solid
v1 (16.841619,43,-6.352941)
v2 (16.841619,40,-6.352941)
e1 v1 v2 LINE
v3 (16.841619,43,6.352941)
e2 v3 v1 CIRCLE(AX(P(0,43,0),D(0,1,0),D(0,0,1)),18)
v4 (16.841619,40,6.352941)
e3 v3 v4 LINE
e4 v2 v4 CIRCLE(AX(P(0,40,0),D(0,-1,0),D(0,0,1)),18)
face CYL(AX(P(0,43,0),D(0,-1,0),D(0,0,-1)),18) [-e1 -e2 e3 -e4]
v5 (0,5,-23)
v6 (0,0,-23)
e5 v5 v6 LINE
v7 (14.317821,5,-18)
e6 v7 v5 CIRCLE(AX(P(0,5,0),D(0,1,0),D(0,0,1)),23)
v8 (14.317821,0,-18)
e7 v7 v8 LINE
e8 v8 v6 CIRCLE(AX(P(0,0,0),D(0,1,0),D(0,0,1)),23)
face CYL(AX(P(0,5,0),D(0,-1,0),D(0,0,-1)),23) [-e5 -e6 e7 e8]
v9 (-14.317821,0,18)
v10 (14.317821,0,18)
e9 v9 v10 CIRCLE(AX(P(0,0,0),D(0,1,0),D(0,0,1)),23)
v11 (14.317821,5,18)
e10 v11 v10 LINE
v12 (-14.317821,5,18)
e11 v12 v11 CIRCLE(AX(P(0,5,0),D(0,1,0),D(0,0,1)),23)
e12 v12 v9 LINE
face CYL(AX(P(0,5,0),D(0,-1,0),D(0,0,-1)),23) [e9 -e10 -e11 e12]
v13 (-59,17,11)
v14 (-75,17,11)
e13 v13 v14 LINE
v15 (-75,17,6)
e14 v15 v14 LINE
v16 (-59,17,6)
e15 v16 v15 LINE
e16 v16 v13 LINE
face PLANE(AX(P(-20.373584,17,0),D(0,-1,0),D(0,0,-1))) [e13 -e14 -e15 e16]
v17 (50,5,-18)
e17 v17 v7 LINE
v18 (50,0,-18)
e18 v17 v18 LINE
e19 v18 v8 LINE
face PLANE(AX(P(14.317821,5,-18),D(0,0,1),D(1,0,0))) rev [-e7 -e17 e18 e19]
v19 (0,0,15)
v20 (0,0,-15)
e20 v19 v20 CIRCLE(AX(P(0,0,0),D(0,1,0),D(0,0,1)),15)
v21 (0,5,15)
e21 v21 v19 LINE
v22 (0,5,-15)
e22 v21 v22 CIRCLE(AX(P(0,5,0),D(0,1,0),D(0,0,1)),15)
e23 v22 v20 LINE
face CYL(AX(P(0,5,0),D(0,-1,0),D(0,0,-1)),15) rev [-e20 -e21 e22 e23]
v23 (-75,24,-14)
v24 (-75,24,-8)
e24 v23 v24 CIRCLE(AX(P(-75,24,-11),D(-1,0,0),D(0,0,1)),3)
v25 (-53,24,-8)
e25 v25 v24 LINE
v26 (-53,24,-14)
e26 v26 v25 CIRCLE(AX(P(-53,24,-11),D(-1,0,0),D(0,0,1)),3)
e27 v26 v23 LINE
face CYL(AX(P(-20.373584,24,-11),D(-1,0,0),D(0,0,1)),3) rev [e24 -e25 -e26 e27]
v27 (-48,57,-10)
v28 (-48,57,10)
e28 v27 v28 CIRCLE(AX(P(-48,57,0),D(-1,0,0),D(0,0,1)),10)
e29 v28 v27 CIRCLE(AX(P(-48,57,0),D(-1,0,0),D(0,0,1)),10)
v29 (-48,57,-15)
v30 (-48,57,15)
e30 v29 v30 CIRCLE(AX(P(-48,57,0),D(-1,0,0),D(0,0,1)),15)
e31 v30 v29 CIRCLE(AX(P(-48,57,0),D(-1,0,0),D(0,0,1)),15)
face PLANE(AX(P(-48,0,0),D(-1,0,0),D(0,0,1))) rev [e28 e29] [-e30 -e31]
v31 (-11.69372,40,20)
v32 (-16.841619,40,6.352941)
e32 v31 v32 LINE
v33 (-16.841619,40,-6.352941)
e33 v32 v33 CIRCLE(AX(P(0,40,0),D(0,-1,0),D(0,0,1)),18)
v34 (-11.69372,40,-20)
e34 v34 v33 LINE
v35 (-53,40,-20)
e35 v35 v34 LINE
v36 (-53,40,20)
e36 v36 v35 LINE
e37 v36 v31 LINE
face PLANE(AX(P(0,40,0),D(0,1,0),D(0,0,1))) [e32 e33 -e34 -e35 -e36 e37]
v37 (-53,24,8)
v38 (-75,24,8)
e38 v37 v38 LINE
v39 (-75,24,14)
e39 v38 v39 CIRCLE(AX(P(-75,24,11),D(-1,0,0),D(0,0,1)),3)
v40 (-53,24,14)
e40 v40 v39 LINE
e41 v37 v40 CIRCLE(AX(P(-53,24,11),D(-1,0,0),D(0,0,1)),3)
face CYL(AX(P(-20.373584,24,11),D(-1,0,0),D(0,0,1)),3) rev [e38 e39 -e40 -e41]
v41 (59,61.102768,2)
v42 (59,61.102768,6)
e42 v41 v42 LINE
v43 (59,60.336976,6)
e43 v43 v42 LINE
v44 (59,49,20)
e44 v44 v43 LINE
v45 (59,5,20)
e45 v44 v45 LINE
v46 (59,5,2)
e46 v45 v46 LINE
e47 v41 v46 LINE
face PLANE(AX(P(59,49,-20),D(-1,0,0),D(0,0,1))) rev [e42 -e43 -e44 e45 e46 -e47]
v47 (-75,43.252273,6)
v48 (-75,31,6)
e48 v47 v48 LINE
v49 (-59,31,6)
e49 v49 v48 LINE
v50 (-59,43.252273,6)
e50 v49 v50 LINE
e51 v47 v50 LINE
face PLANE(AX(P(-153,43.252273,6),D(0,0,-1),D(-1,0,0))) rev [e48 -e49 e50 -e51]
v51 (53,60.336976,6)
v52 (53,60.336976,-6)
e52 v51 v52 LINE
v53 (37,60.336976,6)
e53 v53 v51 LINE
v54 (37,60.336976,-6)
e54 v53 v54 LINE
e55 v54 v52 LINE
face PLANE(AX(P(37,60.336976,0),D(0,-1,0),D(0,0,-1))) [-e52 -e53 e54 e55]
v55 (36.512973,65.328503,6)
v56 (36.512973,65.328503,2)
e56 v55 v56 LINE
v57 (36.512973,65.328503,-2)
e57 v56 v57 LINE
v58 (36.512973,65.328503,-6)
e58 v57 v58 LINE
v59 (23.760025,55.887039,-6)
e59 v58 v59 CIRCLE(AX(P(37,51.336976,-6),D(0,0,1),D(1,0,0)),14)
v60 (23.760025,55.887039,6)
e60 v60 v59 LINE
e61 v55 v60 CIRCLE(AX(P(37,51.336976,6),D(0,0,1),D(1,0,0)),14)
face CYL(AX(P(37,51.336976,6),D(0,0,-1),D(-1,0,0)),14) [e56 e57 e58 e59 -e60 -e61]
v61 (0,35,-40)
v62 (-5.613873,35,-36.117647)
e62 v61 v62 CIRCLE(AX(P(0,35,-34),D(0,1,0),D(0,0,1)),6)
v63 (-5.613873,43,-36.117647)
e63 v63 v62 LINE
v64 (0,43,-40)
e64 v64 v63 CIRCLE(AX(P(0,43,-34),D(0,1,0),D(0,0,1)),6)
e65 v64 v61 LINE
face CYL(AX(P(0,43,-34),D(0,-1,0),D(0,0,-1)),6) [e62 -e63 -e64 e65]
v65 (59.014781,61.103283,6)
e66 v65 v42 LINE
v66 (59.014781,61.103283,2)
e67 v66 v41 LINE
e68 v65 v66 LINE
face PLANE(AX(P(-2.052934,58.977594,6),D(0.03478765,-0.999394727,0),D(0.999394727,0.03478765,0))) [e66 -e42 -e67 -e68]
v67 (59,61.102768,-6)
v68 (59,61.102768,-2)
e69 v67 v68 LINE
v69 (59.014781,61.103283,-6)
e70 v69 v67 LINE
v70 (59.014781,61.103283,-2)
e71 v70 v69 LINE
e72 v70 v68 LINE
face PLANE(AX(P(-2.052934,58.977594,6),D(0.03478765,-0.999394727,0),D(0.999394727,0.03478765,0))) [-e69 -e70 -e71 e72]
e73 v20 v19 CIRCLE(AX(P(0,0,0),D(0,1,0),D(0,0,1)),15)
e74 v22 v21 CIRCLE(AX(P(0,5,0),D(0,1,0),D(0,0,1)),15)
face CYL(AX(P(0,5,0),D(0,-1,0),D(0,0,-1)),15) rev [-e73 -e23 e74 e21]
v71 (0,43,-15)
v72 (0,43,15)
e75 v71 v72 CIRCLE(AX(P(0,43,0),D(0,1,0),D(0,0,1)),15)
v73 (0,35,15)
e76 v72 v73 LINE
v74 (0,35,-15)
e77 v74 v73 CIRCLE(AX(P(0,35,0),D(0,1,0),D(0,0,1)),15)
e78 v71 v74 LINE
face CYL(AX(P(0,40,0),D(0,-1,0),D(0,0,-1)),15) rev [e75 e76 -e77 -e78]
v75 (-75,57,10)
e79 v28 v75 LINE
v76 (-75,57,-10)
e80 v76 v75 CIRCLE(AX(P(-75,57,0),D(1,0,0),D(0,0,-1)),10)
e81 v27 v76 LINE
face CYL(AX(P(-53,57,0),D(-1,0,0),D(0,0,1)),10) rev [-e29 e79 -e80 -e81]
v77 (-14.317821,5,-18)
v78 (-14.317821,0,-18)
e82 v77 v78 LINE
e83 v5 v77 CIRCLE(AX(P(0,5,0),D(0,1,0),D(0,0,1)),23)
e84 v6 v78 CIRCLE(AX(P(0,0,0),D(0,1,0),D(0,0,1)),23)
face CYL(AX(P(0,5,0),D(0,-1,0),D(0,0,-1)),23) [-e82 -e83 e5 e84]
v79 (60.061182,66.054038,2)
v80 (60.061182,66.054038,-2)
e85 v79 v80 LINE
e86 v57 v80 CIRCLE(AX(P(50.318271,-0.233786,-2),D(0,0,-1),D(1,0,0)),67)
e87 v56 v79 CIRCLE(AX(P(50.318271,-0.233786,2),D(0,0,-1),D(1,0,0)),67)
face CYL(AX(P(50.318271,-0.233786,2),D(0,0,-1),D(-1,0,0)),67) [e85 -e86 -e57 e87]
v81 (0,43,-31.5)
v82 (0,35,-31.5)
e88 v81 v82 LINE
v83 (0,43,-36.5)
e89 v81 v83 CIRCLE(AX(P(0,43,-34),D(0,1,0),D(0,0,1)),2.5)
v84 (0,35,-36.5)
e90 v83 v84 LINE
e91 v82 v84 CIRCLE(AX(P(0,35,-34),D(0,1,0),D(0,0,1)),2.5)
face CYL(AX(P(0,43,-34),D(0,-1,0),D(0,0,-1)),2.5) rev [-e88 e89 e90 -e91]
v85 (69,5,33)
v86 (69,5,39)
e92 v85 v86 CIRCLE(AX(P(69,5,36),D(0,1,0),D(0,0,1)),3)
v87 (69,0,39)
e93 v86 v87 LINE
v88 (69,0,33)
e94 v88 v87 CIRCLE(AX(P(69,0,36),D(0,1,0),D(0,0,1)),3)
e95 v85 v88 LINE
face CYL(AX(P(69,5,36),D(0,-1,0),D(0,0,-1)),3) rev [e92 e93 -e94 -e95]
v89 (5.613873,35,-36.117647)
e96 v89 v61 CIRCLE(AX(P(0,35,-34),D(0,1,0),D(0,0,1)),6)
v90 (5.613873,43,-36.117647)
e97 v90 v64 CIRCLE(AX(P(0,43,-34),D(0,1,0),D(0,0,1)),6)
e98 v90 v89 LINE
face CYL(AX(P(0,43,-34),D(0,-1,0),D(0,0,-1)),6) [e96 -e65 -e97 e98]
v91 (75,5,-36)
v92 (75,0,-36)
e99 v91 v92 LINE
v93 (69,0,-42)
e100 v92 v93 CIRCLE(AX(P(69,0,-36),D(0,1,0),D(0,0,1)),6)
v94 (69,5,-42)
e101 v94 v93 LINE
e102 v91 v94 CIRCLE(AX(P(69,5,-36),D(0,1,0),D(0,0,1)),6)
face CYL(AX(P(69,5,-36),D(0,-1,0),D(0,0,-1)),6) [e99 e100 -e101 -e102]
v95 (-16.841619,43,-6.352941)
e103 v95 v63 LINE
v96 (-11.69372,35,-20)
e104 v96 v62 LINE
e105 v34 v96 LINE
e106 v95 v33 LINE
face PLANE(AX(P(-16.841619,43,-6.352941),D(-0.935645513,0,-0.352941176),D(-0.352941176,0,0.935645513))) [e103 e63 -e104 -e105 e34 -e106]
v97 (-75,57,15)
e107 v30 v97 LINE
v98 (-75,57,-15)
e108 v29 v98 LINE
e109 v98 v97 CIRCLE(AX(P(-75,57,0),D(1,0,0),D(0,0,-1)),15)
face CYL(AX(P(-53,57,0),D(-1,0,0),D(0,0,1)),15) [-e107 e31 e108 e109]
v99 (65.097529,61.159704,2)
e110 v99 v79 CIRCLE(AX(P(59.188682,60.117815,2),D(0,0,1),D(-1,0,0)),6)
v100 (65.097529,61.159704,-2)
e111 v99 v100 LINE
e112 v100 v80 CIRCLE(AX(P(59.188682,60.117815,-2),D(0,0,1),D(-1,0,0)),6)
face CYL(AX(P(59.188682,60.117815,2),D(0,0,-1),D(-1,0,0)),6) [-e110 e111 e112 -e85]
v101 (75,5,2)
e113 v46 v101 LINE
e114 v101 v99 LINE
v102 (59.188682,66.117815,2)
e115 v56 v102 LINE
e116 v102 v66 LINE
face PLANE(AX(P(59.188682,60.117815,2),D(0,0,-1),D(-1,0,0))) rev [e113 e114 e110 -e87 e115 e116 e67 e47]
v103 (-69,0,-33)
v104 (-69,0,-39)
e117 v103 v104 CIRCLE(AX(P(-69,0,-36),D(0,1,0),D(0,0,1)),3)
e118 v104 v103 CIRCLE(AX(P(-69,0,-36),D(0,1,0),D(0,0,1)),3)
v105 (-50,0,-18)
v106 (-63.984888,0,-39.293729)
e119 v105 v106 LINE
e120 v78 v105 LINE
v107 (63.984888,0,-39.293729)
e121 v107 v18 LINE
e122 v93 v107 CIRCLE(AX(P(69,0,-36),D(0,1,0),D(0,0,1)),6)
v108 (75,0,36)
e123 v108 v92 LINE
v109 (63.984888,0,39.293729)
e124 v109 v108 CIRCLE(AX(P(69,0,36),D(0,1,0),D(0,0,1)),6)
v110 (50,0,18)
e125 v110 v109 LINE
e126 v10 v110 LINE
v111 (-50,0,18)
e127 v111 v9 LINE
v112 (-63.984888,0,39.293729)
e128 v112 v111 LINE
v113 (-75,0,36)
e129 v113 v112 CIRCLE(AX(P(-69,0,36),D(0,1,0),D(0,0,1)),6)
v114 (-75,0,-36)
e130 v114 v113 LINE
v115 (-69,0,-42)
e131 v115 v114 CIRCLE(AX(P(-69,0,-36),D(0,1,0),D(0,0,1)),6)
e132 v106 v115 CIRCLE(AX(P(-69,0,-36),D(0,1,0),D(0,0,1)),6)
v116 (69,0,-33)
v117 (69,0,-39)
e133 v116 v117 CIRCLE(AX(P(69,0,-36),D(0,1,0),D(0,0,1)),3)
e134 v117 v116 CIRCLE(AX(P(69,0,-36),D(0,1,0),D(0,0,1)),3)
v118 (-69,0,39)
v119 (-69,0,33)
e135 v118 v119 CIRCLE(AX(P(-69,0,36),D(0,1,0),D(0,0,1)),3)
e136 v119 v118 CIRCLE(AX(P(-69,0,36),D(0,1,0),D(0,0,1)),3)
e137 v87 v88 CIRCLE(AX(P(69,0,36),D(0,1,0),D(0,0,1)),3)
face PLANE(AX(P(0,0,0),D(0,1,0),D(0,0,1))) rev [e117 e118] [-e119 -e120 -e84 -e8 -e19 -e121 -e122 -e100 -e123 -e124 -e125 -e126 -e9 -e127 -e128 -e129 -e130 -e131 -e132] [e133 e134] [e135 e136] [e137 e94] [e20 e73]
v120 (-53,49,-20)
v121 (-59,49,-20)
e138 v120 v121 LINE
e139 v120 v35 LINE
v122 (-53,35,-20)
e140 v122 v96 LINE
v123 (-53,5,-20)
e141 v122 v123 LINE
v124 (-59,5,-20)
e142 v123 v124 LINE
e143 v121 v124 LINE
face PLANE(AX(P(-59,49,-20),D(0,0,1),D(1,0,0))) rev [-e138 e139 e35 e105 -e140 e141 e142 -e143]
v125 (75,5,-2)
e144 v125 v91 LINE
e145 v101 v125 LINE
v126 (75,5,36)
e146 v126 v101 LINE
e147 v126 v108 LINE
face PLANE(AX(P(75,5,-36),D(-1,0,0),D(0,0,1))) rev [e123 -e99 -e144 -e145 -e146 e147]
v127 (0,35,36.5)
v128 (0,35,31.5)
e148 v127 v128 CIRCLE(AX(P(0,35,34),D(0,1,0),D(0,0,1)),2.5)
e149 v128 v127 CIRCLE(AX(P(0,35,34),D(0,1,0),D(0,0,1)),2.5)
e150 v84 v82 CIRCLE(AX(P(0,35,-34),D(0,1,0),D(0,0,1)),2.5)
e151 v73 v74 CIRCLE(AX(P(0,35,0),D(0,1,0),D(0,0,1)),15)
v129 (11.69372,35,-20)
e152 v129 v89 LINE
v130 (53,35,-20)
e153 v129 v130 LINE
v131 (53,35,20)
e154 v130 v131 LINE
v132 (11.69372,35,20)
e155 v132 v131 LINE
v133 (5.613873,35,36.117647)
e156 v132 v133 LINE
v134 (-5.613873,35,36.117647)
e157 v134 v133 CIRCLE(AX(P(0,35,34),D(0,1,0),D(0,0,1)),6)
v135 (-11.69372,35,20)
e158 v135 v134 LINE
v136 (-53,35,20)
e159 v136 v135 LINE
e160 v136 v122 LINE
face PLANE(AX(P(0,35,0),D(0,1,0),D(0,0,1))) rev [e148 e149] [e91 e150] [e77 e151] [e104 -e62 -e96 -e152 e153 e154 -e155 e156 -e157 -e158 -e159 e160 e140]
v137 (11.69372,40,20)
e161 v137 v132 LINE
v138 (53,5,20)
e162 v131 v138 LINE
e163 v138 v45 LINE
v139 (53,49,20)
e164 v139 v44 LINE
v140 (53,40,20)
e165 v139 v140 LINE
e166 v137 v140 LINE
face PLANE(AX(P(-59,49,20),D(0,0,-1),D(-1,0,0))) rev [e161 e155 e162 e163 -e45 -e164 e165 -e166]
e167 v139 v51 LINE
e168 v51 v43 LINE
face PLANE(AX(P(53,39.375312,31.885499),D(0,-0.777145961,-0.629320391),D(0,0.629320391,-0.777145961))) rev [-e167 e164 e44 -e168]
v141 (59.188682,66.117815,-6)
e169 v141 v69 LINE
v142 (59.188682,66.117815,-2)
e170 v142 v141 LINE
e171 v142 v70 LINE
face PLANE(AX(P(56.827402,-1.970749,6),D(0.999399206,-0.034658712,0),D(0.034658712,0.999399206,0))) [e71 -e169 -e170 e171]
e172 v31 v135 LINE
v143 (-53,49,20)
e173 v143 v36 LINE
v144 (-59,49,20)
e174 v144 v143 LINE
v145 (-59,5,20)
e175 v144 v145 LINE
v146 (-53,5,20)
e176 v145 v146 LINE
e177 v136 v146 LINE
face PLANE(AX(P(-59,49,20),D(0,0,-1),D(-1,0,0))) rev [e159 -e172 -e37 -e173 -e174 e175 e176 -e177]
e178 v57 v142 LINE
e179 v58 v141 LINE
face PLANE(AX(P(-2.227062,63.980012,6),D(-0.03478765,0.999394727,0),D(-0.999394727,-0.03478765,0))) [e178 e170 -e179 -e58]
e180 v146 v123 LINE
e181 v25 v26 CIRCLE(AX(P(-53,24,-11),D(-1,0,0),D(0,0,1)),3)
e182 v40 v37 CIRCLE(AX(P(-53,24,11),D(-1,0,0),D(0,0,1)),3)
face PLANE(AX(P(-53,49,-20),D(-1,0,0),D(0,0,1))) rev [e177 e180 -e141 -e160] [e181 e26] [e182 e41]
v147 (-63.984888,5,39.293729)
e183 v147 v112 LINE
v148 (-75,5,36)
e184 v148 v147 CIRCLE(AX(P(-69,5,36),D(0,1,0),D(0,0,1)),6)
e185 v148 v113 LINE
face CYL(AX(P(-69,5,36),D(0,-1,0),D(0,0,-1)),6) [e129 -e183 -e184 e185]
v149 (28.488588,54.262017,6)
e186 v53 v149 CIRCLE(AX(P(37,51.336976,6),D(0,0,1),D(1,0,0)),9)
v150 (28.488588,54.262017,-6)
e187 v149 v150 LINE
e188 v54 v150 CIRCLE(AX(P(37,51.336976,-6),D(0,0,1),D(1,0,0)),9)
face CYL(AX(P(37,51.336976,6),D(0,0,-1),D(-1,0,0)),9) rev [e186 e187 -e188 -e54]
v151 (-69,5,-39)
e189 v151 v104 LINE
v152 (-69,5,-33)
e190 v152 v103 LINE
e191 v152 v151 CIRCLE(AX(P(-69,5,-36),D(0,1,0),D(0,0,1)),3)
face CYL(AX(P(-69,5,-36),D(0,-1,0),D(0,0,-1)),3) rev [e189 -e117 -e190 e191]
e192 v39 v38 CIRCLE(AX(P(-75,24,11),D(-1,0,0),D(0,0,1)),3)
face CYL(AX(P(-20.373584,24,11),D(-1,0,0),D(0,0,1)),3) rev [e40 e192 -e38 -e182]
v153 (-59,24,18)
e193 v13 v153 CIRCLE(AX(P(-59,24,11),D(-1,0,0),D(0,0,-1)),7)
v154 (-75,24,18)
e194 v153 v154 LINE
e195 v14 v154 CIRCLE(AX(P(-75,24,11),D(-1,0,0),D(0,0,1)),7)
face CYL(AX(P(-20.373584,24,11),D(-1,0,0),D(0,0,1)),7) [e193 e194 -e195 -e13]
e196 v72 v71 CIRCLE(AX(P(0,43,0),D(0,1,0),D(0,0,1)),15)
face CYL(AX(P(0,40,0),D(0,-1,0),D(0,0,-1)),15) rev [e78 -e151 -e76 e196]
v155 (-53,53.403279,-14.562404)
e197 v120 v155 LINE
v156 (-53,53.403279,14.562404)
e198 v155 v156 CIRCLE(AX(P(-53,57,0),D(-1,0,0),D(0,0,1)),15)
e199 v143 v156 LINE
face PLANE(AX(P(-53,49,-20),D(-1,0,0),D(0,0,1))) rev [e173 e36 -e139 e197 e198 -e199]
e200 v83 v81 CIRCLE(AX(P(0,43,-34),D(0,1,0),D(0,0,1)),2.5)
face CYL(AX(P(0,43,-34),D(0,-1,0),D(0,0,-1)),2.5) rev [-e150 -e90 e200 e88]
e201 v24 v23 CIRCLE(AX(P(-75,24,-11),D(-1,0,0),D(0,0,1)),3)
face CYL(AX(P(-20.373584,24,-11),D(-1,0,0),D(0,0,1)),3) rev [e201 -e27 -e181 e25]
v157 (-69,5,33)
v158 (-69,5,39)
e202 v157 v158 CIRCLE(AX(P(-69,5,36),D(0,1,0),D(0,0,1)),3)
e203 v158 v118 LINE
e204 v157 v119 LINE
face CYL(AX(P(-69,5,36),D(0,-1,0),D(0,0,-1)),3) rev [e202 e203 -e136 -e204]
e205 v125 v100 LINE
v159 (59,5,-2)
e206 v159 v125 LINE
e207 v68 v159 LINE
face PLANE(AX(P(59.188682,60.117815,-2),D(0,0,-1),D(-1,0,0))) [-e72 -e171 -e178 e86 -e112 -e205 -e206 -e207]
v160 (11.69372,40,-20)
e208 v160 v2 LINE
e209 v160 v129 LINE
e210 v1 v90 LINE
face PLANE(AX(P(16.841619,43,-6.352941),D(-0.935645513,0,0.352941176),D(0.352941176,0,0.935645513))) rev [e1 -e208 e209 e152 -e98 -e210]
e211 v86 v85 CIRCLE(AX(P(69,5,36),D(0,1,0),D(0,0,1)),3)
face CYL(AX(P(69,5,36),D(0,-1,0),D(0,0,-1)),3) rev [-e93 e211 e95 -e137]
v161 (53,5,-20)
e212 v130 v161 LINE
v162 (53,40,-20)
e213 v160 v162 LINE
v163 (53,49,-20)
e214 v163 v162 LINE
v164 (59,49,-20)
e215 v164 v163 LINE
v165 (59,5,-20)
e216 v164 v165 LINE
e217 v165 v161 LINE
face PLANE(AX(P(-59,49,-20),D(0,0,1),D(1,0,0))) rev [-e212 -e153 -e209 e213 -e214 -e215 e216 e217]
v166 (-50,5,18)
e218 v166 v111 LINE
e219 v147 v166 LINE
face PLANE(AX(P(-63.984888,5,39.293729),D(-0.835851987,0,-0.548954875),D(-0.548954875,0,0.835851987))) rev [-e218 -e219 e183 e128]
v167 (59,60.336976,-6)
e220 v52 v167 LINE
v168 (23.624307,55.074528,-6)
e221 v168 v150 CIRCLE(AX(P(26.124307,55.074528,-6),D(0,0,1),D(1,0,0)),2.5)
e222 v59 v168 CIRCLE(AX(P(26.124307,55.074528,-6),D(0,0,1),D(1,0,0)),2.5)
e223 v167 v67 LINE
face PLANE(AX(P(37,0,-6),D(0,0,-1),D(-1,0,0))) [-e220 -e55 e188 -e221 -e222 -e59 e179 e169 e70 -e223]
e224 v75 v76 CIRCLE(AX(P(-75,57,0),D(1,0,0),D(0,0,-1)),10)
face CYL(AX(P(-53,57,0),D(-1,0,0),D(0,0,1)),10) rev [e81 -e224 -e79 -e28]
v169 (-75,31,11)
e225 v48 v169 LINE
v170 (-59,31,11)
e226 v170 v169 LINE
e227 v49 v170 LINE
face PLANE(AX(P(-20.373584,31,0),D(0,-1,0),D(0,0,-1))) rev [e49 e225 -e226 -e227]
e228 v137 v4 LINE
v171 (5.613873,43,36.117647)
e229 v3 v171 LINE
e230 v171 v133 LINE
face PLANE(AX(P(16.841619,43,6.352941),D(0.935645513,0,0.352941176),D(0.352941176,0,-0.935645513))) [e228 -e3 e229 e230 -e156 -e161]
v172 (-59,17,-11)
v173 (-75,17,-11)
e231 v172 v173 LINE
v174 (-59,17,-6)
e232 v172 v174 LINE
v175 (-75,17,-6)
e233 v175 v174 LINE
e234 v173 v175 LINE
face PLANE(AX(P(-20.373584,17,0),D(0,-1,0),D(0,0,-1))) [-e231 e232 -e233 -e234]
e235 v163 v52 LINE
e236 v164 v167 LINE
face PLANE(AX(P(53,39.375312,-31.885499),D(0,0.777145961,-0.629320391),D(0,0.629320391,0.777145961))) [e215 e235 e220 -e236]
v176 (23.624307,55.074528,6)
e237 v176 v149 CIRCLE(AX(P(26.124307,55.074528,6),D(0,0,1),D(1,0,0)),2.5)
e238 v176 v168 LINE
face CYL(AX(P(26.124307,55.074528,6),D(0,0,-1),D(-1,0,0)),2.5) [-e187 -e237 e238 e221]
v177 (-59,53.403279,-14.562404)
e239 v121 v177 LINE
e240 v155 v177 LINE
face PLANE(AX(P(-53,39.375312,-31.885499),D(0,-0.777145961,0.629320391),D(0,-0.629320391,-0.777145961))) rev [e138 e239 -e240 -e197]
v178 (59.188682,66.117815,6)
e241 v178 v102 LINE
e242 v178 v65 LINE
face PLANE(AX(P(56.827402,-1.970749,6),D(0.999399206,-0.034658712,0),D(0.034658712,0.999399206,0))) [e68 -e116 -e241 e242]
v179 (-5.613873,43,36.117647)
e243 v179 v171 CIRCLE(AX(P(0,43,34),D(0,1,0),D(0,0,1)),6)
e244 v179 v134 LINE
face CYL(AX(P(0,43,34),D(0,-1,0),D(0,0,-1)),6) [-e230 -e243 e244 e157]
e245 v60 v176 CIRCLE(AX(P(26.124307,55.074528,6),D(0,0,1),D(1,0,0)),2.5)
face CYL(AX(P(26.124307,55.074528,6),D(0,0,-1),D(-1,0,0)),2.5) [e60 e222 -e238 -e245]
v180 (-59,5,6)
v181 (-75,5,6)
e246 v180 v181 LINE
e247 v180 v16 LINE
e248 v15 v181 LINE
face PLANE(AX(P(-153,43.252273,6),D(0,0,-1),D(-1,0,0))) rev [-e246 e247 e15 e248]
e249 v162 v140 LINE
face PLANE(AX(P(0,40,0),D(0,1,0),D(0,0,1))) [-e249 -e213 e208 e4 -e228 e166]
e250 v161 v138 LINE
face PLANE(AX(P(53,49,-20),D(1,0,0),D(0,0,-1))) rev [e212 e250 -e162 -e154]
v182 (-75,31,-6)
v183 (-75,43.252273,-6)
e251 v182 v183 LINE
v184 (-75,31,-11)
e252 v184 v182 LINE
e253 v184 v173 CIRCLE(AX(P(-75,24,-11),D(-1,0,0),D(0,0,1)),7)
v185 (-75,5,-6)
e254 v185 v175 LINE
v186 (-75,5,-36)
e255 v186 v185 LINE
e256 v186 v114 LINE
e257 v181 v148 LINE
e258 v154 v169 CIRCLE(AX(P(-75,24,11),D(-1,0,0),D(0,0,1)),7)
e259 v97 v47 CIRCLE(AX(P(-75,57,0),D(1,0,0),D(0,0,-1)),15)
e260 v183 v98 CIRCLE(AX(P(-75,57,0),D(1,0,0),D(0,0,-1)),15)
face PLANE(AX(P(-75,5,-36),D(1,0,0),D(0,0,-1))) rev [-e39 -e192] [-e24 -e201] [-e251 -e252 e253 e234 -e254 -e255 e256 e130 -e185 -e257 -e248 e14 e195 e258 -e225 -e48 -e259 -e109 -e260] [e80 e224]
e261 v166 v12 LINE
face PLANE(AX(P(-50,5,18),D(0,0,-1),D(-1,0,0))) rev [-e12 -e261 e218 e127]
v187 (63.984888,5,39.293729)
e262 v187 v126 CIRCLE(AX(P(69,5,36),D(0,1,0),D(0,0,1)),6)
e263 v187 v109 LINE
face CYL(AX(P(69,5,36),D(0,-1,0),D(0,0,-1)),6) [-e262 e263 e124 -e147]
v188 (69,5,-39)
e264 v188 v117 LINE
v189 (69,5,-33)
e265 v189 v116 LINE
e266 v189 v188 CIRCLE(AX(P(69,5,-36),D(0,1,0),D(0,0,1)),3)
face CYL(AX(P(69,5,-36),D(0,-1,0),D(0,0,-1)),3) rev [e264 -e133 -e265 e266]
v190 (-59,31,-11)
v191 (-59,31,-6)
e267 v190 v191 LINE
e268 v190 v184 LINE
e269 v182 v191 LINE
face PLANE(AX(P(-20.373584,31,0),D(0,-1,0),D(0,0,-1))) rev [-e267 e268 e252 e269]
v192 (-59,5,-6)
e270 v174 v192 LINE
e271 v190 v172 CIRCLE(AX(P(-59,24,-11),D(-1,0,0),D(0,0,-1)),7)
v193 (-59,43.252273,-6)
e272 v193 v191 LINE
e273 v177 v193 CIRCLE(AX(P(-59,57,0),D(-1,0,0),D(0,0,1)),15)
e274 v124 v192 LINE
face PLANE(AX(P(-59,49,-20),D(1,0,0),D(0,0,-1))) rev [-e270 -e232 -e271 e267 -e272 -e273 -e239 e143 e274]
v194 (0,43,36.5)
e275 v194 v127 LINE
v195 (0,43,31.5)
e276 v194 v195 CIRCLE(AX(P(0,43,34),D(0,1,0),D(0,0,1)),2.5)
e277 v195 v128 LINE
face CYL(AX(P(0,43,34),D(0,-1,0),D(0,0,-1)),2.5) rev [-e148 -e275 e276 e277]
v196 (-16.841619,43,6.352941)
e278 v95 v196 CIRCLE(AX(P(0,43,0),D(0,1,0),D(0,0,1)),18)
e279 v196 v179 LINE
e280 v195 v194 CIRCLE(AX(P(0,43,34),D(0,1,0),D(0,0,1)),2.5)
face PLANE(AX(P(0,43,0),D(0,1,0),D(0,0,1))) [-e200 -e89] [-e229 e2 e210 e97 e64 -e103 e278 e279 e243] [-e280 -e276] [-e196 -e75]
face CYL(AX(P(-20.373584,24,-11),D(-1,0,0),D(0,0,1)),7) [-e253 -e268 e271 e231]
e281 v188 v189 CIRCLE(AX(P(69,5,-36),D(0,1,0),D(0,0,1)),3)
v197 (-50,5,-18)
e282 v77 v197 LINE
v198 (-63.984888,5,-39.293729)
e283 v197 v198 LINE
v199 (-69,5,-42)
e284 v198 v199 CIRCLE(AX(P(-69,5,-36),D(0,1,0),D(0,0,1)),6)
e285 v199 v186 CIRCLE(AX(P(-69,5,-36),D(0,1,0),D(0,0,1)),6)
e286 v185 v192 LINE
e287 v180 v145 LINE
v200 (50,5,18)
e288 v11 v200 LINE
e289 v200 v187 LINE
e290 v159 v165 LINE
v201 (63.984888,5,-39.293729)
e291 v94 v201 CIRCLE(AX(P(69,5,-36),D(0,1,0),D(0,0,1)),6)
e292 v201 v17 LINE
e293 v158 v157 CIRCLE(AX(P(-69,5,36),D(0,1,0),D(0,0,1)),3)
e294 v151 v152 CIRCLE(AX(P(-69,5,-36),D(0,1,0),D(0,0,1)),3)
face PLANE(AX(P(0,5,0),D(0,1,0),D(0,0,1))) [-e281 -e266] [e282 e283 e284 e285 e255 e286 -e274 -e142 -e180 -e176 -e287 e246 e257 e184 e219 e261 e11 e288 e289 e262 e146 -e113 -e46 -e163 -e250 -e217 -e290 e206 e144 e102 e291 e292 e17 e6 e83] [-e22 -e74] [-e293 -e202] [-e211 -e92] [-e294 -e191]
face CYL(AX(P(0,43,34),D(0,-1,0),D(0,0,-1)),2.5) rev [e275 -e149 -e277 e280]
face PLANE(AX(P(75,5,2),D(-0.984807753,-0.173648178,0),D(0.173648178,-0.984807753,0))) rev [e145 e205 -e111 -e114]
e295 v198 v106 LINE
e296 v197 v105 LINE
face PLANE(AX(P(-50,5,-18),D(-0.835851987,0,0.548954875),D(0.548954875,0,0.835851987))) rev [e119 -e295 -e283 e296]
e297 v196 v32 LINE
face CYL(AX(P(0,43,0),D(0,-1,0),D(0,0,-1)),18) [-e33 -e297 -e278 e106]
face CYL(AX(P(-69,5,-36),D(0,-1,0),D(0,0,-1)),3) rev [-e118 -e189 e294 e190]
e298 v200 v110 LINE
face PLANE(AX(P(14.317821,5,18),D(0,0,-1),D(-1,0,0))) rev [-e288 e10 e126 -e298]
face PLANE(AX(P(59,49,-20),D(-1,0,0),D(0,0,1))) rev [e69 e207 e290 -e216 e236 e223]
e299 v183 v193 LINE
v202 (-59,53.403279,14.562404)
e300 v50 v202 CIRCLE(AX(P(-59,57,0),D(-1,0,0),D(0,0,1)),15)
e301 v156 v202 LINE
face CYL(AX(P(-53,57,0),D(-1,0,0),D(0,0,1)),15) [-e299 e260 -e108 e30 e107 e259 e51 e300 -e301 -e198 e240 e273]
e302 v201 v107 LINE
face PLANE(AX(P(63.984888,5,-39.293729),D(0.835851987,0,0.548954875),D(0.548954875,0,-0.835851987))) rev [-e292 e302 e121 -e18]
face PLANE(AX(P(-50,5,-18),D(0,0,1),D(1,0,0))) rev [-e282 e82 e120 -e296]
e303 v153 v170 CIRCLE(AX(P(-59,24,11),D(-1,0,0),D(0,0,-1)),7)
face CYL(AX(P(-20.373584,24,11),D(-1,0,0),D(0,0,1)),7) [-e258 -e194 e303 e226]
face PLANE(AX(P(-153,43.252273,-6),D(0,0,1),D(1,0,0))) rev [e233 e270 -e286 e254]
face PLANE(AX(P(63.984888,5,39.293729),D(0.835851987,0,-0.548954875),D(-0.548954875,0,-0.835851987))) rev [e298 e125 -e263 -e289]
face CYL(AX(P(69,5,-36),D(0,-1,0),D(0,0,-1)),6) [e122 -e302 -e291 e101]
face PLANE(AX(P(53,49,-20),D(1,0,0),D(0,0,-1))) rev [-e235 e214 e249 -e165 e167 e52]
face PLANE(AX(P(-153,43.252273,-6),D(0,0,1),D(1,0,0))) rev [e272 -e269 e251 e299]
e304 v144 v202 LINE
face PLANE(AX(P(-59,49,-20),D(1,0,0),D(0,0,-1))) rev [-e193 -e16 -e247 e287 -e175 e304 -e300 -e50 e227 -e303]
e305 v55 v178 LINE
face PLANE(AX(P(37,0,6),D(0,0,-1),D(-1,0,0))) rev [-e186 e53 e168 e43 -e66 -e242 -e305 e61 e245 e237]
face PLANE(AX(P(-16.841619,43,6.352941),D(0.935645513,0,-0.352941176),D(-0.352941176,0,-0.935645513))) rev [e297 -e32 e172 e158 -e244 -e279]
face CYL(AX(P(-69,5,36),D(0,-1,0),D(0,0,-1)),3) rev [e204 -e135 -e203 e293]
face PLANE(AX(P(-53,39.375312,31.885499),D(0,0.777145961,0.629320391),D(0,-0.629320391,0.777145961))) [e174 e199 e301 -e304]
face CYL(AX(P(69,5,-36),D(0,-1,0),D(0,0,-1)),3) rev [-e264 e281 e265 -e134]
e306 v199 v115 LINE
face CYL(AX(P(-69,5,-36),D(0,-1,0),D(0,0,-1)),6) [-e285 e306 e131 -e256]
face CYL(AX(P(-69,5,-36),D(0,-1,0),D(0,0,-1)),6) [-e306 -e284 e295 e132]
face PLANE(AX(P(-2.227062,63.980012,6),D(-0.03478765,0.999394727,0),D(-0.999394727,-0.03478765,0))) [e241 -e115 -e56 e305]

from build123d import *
from build123d.topology import SkipClean

# Parameters (mm, degrees)
BASE_PLATE_SKETCH_R           = 15
BASE_PLATE_SKETCH_R_2         = 3
BASE_PLATE_DEPTH              = 5
CENTER_PEDESTAL_SKETCH_W      = 6
CENTER_PEDESTAL_SKETCH_H      = 40
CENTER_PEDESTAL_DEPTH         = 44
MID_FLANGE_PLATE_DEPTH        = 6
MID_FLANGE_BOSS_11MM_DEPTH    = 11
FLANGE_START                  = 16
FLANGE_WEB_SKETCH_R           = 10
FLANGE_WEB_DEPTH              = 16
CENTER_BORE_SKETCH_R          = 10
CENTER_BORE_CUT_DEPTH         = 50
UPPER_BRACKET_SKETCH_W        = 12
UPPER_BRACKET_SKETCH_H        = 11.336976465
UPPER_BRACKET_SKETCH_W_2      = 14
UPPER_BRACKET_SKETCH_H_2      = 44
UPPER_BRACKET_SKETCH_H_3      = 5
UPPER_BRACKET_PLATE_DEPTH     = 6
SKETCH6_3_W                   = 12
SKETCH6_3_H                   = 2
UPPER_BRACKET_WALL_22MM_DEPTH = 22
SUPPORT_RIB_DEPTH             = 2
SIDE_BRACKET_BLOCK_12MM_DEPTH = 6
SIDE_BRACKET_LIP_4MM_DEPTH    = 2
TOP_MOUNT_SKETCH_W            = 118
TOP_MOUNT_SKETCH_H            = 40
TOP_MOUNT_SKETCH_R            = 15
TOP_MOUNT_PLATE_5MM_DEPTH     = 5
SKETCH9_3_R                   = 6
SKETCH9_3_R_2                 = 2.5
SKETCH9_3_R_3                 = 18
SKETCH9_3_R_4                 = 15
TOP_MOUNT_TABS_8MM_DEPTH      = 8
TUBE_BOSS_SKETCH_R            = 3
TUBE_BOSS_DEPTH               = 16
TUBE_BORE_SKETCH_R            = 3
TUBE_BORE_CUT_DEPTH           = 50


with BuildPart() as part:
    # Base Plate Sketch → Base Plate (new body)
    with BuildSketch(Plane(origin=(0, 0, 0), x_dir=(1, 0, 0), z_dir=(0, 1, 0))):
        with BuildLine():
            Line((14.317821063, 18), (50, 18))
            Line((50, 18), (63.984888076, 39.293729253))
            ThreePointArc((63.984888076, 39.293729253), (70.718913677, 41.748507265), (75, 36))
            Line((75, 36), (75, -36))
            ThreePointArc((75, -36), (70.718913677, -41.748507265), (63.984888076, -39.293729253))
            Line((63.984888076, -39.293729253), (50, -18))
            Line((50, -18), (14.317821063, -18))
            ThreePointArc((14.317821063, -18), (0, -23), (-14.317821063, -18))
            Line((-14.317821063, -18), (-50, -18))
            Line((-50, -18), (-63.984888076, -39.293729253))
            ThreePointArc((-63.984888076, -39.293729253), (-70.718913677, -41.748507265), (-75, -36))
            Line((-75, -36), (-75, 36))
            ThreePointArc((-75, 36), (-70.718913677, 41.748507265), (-63.984888076, 39.293729253))
            Line((-63.984888076, 39.293729253), (-50, 18))
            Line((-50, 18), (-14.317821063, 18))
            ThreePointArc((-14.317821063, 18), (0, 23), (14.317821063, 18))
        make_face()
        with Locations(Location((0, 0, 0), (0, 0, 270))):
            Circle(BASE_PLATE_SKETCH_R, mode=Mode.SUBTRACT)
        with Locations(Location((-69, 36, 0), (0, 0, 270))):
            Circle(BASE_PLATE_SKETCH_R_2, mode=Mode.SUBTRACT)
        with Locations(Location((-69, -36, 0), (0, 0, 270))):
            Circle(BASE_PLATE_SKETCH_R_2, mode=Mode.SUBTRACT)
        with Locations(Location((69, 36, 0), (0, 0, 270))):
            Circle(BASE_PLATE_SKETCH_R_2, mode=Mode.SUBTRACT)
        with Locations(Location((69, -36, 0), (0, 0, 270))):
            Circle(BASE_PLATE_SKETCH_R_2, mode=Mode.SUBTRACT)
    extrude(amount=BASE_PLATE_DEPTH)

    # Center Pedestal Sketch → Center Pedestal (add)
    with BuildSketch(Plane(origin=(0, 5, 0), x_dir=(1, 0, 0), z_dir=(0, 1, 0))):
        with Locations((-56, 0)):
            Rectangle(CENTER_PEDESTAL_SKETCH_W, CENTER_PEDESTAL_SKETCH_H)
        with Locations((56, 0)):
            Rectangle(CENTER_PEDESTAL_SKETCH_W, CENTER_PEDESTAL_SKETCH_H)
    extrude(amount=CENTER_PEDESTAL_DEPTH)

    # Mid Flange Sketch → Mid Flange Plate (add)
    with BuildSketch(Plane.ZY.offset(59)):
        with BuildLine():
            ThreePointArc((6.545818153, 70.496379689), (-9.439805866, 68.657189422), (-14.562403531, 53.403278799))
            ThreePointArc((-14.562403531, 53.403278799), (-13.802217517, 51.126432803), (-12.68857754, 49))
            Line((-12.68857754, 49), (-6, 49))
            ThreePointArc((-6, 49), (-4.472135955, 65.94427191), (10, 57))
            ThreePointArc((10, 57), (8.94427191, 52.527864045), (6, 49))
            Line((6, 49), (12.68857754, 49))
            ThreePointArc((12.68857754, 49), (13.802217517, 51.126432803), (14.562403531, 53.403278799))
            ThreePointArc((14.562403531, 53.403278799), (14.890199008, 55.188378208), (15, 57))
            ThreePointArc((15, 57), (12.711948558, 64.962811303), (6.545818153, 70.496379689))
        make_face()
        with BuildLine():
            Line((-6, 49), (-12.68857754, 49))
            ThreePointArc((-12.68857754, 49), (0, 42), (12.68857754, 49))
            Line((12.68857754, 49), (6, 49))
            ThreePointArc((6, 49), (0, 47), (-6, 49))
        make_face()
        with BuildLine():
            Line((-14.562403531, 53.403278799), (-20, 49))
            Line((-20, 49), (-12.68857754, 49))
            ThreePointArc((-12.68857754, 49), (-13.802217517, 51.126432803), (-14.562403531, 53.403278799))
        make_face()
        with BuildLine():
            ThreePointArc((6.545818153, 70.496379689), (-9.439805866, 68.657189422), (-14.562403531, 53.403278799))
            ThreePointArc((-14.562403531, 53.403278799), (-13.802217517, 51.126432803), (-12.68857754, 49))
            Line((-12.68857754, 49), (-6, 49))
            ThreePointArc((-6, 49), (-4.472135955, 65.94427191), (10, 57))
            ThreePointArc((10, 57), (8.94427191, 52.527864045), (6, 49))
            Line((6, 49), (12.68857754, 49))
            ThreePointArc((12.68857754, 49), (13.802217517, 51.126432803), (14.562403531, 53.403278799))
            ThreePointArc((14.562403531, 53.403278799), (14.890199008, 55.188378208), (15, 57))
            ThreePointArc((15, 57), (12.711948558, 64.962811303), (6.545818153, 70.496379689))
        make_face()
        with BuildLine():
            Line((-6, 49), (-12.68857754, 49))
            ThreePointArc((-12.68857754, 49), (0, 42), (12.68857754, 49))
            Line((12.68857754, 49), (6, 49))
            ThreePointArc((6, 49), (0, 47), (-6, 49))
        make_face()
        with BuildLine():
            ThreePointArc((14.562403531, 53.403278799), (13.802217517, 51.126432803), (12.68857754, 49))
            Line((12.68857754, 49), (20, 49))
            Line((20, 49), (14.562403531, 53.403278799))
        make_face()
    extrude(amount=-MID_FLANGE_PLATE_DEPTH)

    # Sketch3_3 → Mid Flange Boss 11mm (add)
    with BuildSketch(Plane.ZY.offset(59)):
        with BuildLine():
            ThreePointArc((6.545818153, 70.496379689), (-9.439805866, 68.657189422), (-14.562403531, 53.403278799))
            ThreePointArc((-14.562403531, 53.403278799), (-13.802217517, 51.126432803), (-12.68857754, 49))
            Line((-12.68857754, 49), (-6, 49))
            ThreePointArc((-6, 49), (-4.472135955, 65.94427191), (10, 57))
            ThreePointArc((10, 57), (8.94427191, 52.527864045), (6, 49))
            Line((6, 49), (12.68857754, 49))
            ThreePointArc((12.68857754, 49), (13.802217517, 51.126432803), (14.562403531, 53.403278799))
            ThreePointArc((14.562403531, 53.403278799), (14.890199008, 55.188378208), (15, 57))
            ThreePointArc((15, 57), (12.711948558, 64.962811303), (6.545818153, 70.496379689))
        make_face()
        with BuildLine():
            Line((-6, 49), (-12.68857754, 49))
            ThreePointArc((-12.68857754, 49), (0, 42), (12.68857754, 49))
            Line((12.68857754, 49), (6, 49))
            ThreePointArc((6, 49), (0, 47), (-6, 49))
        make_face()
        with BuildLine():
            ThreePointArc((6.545818153, 70.496379689), (-9.439805866, 68.657189422), (-14.562403531, 53.403278799))
            ThreePointArc((-14.562403531, 53.403278799), (-13.802217517, 51.126432803), (-12.68857754, 49))
            Line((-12.68857754, 49), (-6, 49))
            ThreePointArc((-6, 49), (-4.472135955, 65.94427191), (10, 57))
            ThreePointArc((10, 57), (8.94427191, 52.527864045), (6, 49))
            Line((6, 49), (12.68857754, 49))
            ThreePointArc((12.68857754, 49), (13.802217517, 51.126432803), (14.562403531, 53.403278799))
            ThreePointArc((14.562403531, 53.403278799), (14.890199008, 55.188378208), (15, 57))
            ThreePointArc((15, 57), (12.711948558, 64.962811303), (6.545818153, 70.496379689))
        make_face()
        with BuildLine():
            Line((-6, 49), (-12.68857754, 49))
            ThreePointArc((-12.68857754, 49), (0, 42), (12.68857754, 49))
            Line((12.68857754, 49), (6, 49))
            ThreePointArc((6, 49), (0, 47), (-6, 49))
        make_face()
    extrude(amount=-MID_FLANGE_BOSS_11MM_DEPTH)

    # Flange Web Sketch → Flange Web (add)
    with SkipClean():  # the faces are left unmerged after this step: merging them gives an invalid solid
        with BuildSketch(Plane.ZY.offset(59).offset(FLANGE_START)):
            with BuildLine():
                Line((-6, 0), (6, 0))
                Line((6, 0), (6, 43.252272915))
                ThreePointArc((6, 43.252272915), (0, 72), (-6, 43.252272915))
                Line((-6, 43.252272915), (-6, 0))
            make_face()
            with Locations((0, 57)):
                Circle(FLANGE_WEB_SKETCH_R, mode=Mode.SUBTRACT)
        extrude(amount=-FLANGE_WEB_DEPTH)

    # Center Bore Sketch → Center Bore Cut (cut)
    with SkipClean():  # the faces are left unmerged after this step: merging them gives an invalid solid
        with BuildSketch(Plane.ZY.offset(75)):
            with Locations((0, 57)):
                Circle(CENTER_BORE_SKETCH_R)
        extrude(amount=-CENTER_BORE_CUT_DEPTH, mode=Mode.SUBTRACT)

    # Upper Bracket Sketch → Upper Bracket Plate (add)
    with SkipClean():  # the faces are left unmerged after this step: merging them gives an invalid solid
        with BuildSketch(Plane(origin=(59, 0, 0), x_dir=(0, 0, -1), z_dir=(1, 0, 0))):
            with Locations((0, 54.668488233)):
                Rectangle(UPPER_BRACKET_SKETCH_W, UPPER_BRACKET_SKETCH_H)
            Polygon((-20, 49), (-6, 49), (-6, 60.336976465), align=None)
            Polygon((6, 60.336976465), (6, 49), (20, 49), align=None)
            with Locations((-13, 27)):
                Rectangle(UPPER_BRACKET_SKETCH_W_2, UPPER_BRACKET_SKETCH_H_2)
            with Locations((0, 27)):
                Rectangle(UPPER_BRACKET_SKETCH_W, UPPER_BRACKET_SKETCH_H_2)
            with Locations((13, 27)):
                Rectangle(UPPER_BRACKET_SKETCH_W_2, UPPER_BRACKET_SKETCH_H_2)
            with Locations((0, 2.5)):
                Rectangle(UPPER_BRACKET_SKETCH_W, UPPER_BRACKET_SKETCH_H_3)
        extrude(amount=-UPPER_BRACKET_PLATE_DEPTH)

    # Sketch6_3 → Upper Bracket Wall 22mm (add)
    with SkipClean():  # the faces are left unmerged after this step: merging them gives an invalid solid
        with BuildSketch(Plane(origin=(59, 0, 0), x_dir=(0, 0, -1), z_dir=(1, 0, 0))):
            with Locations((0, 61.336976465)):
                Rectangle(SKETCH6_3_W, SKETCH6_3_H)
        extrude(amount=-UPPER_BRACKET_WALL_22MM_DEPTH)

    # Support Rib Sketch → Support Rib (add, symmetric)
    with SkipClean():  # the faces are left unmerged after this step: merging them gives an invalid solid
        with BuildSketch(Plane.XY):
            with BuildLine():
                Line((75, 5), (65.097528939, 61.159704097))
                ThreePointArc((65.097528939, 61.159704097), (63.045408079, 64.714081689), (59.188682421, 66.117815031))
                ThreePointArc((59.188682421, 66.117815031), (47.934434691, 65.165842314), (37, 62.336976465))
                Line((37, 62.336976465), (59, 62.336976465))
                Line((59, 62.336976465), (59, 5))
                Line((59, 5), (75, 5))
            make_face()
        extrude(amount=SUPPORT_RIB_DEPTH, both=True)

    # Side Bracket Sketch → Side Bracket Block 12mm (add, symmetric)
    with SkipClean():  # the faces are left unmerged after this step: merging them gives an invalid solid
        with BuildSketch(Plane.XY):
            with BuildLine():
                Line((36.512972901, 65.328502636), (59.188682421, 66.117815031))
                Line((59.188682421, 66.117815031), (59.014780713, 61.103282774))
                Line((59.014780713, 61.103282774), (37, 60.336976465))
                ThreePointArc((37, 60.336976465), (31.771489867, 58.662458141), (28.488587739, 54.262016862))
                ThreePointArc((28.488587739, 54.262016862), (25.311795334, 52.7102469), (23.760025372, 55.887039305))
                ThreePointArc((23.760025372, 55.887039305), (28.669756813, 62.588956221), (36.512972901, 65.328502636))
            make_face()
        extrude(amount=SIDE_BRACKET_BLOCK_12MM_DEPTH, both=True)

    # Sketch8_6 → Side Bracket Lip 4mm (add, symmetric)
    with SkipClean():  # the faces are left unmerged after this step: merging them gives an invalid solid
        with BuildSketch(Plane.XY):
            with BuildLine():
                ThreePointArc((60.061181917, 66.054038125), (63.370223983, 64.420687346), (65.097528939, 61.159704097))
                Line((65.097528939, 61.159704097), (75, 5))
                Line((75, 5), (59, 5))
                Line((59, 5), (59.188682421, 66.117815031))
                Line((59.188682421, 66.117815031), (36.512972901, 65.328502636))
                ThreePointArc((36.512972901, 65.328502636), (48.254936842, 66.734434783), (60.061181917, 66.054038125))
            make_face()
        extrude(amount=SIDE_BRACKET_LIP_4MM_DEPTH, both=True)

    # Top Mount Sketch → Top Mount Plate 5mm (add)
    with SkipClean():  # the faces are left unmerged after this step: merging them gives an invalid solid
        with BuildSketch(Plane(origin=(0, 35, 0), x_dir=(1, 0, 0), z_dir=(0, 1, 0))):
            Rectangle(TOP_MOUNT_SKETCH_W, TOP_MOUNT_SKETCH_H)
            with Locations(Location((0, 0, 0), (0, 0, 270))):
                Circle(TOP_MOUNT_SKETCH_R, mode=Mode.SUBTRACT)
        extrude(amount=TOP_MOUNT_PLATE_5MM_DEPTH)

    # Sketch9_3 → Top Mount Tabs 8mm (add)
    # profile 1 of 7: a face of its own
    with SkipClean():  # the faces are left unmerged after this step: merging them gives an invalid solid
        with BuildSketch(Plane(origin=(0, 35, 0), x_dir=(1, 0, 0), z_dir=(0, 1, 0))):
            with Locations((0, 34)):
                Circle(SKETCH9_3_R)
            with Locations(Location((0, 34, 0), (0, 0, 270))):
                Circle(SKETCH9_3_R_2, mode=Mode.SUBTRACT)
        # profile 2 of 7: a face of its own
        with BuildSketch(Plane(origin=(0, 35, 0), x_dir=(1, 0, 0), z_dir=(0, 1, 0))):
            with BuildLine():
                Line((-5.613873078, 36.117647059), (-11.69371981, 20))
                Line((-11.69371981, 20), (11.69371981, 20))
                Line((11.69371981, 20), (5.613873078, 36.117647059))
                ThreePointArc((5.613873078, 36.117647059), (5.902678988, 35.076280989), (6, 34))
                ThreePointArc((6, 34), (-1.076280989, 28.097321012), (-5.613873078, 36.117647059))
            make_face()
        # profile 3 of 7: a face of its own
        with BuildSketch(Plane(origin=(0, 35, 0), x_dir=(1, 0, 0), z_dir=(0, 1, 0))):
            Circle(SKETCH9_3_R_3)
            with Locations(Location((0, 0, 0), (0, 0, 270))):
                Circle(SKETCH9_3_R_4, mode=Mode.SUBTRACT)
        # profile 4 of 7: a face of its own
        with BuildSketch(Plane(origin=(0, 35, 0), x_dir=(1, 0, 0), z_dir=(0, 1, 0))):
            with BuildLine():
                Line((11.69371981, 20), (-11.69371981, 20))
                Line((-11.69371981, 20), (-16.841619234, 6.352941176))
                ThreePointArc((-16.841619234, 6.352941176), (0, 18), (16.841619234, 6.352941176))
                Line((16.841619234, 6.352941176), (11.69371981, 20))
            make_face()
        # profile 5 of 7: a face of its own
        with BuildSketch(Plane(origin=(0, 35, 0), x_dir=(1, 0, 0), z_dir=(0, 1, 0))):
            with BuildLine():
                Line((-16.841619234, -6.352941176), (-11.69371981, -20))
                Line((-11.69371981, -20), (11.69371981, -20))
                Line((11.69371981, -20), (16.841619234, -6.352941176))
                ThreePointArc((16.841619234, -6.352941176), (0, -18), (-16.841619234, -6.352941176))
            make_face()
        # profile 6 of 7: a face of its own
        with BuildSketch(Plane(origin=(0, 35, 0), x_dir=(1, 0, 0), z_dir=(0, 1, 0))):
            with BuildLine():
                Line((11.69371981, -20), (-11.69371981, -20))
                Line((-11.69371981, -20), (-5.613873078, -36.117647059))
                ThreePointArc((-5.613873078, -36.117647059), (-1.076280989, -28.097321012), (6, -34))
                ThreePointArc((6, -34), (5.902678988, -35.076280989), (5.613873078, -36.117647059))
                Line((5.613873078, -36.117647059), (11.69371981, -20))
            make_face()
        # profile 7 of 7: a face of its own
        with BuildSketch(Plane(origin=(0, 35, 0), x_dir=(1, 0, 0), z_dir=(0, 1, 0))):
            with Locations((0, -34)):
                Circle(SKETCH9_3_R)
            with Locations(Location((0, -34, 0), (0, 0, 270))):
                Circle(SKETCH9_3_R_2, mode=Mode.SUBTRACT)
        extrude(amount=TOP_MOUNT_TABS_8MM_DEPTH)

    # Tube Boss Sketch → Tube Boss (add)
    # profile 1 of 9: a face of its own
    with SkipClean():  # the faces are left unmerged after this step: merging them gives an invalid solid
        with BuildSketch(Plane.ZY.offset(75)):
            with BuildLine():
                ThreePointArc((-6, 28.898979486), (-8.288252998, 30.453404388), (-11, 31))
                ThreePointArc((-11, 31), (-18, 24), (-11, 17))
                ThreePointArc((-11, 17), (-8.288252998, 17.546595612), (-6, 19.101020514))
                Line((-6, 19.101020514), (-6, 28.898979486))
            make_face()
            with Locations((-11, 24)):
                Circle(TUBE_BOSS_SKETCH_R, mode=Mode.SUBTRACT)
        # profile 2 of 9: a face of its own
        with BuildSketch(Plane.ZY.offset(75)):
            with BuildLine():
                Line((6, 31), (-6, 31))
                Line((-6, 31), (-6, 28.898979486))
                ThreePointArc((-6, 28.898979486), (-4.519259302, 26.645751311), (-4, 24))
                ThreePointArc((-4, 24), (-4.519259302, 21.354248689), (-6, 19.101020514))
                Line((-6, 19.101020514), (-6, 17))
                Line((-6, 17), (6, 17))
                Line((6, 17), (6, 19.101020514))
                ThreePointArc((6, 19.101020514), (4, 24), (6, 28.898979486))
                Line((6, 28.898979486), (6, 31))
            make_face()
        # profile 3 of 9: a face of its own
        with BuildSketch(Plane.ZY.offset(75)):
            with BuildLine():
                Line((-6, 31), (-11, 31))
                ThreePointArc((-11, 31), (-8.288252998, 30.453404388), (-6, 28.898979486))
                Line((-6, 28.898979486), (-6, 31))
            make_face()
        # profile 4 of 9: a face of its own
        with BuildSketch(Plane.ZY.offset(75)):
            with BuildLine():
                ThreePointArc((-4, 24), (-4.519259302, 26.645751311), (-6, 28.898979486))
                Line((-6, 28.898979486), (-6, 19.101020514))
                ThreePointArc((-6, 19.101020514), (-4.519259302, 21.354248689), (-4, 24))
            make_face()
        # profile 5 of 9: a face of its own
        with BuildSketch(Plane.ZY.offset(75)):
            with BuildLine():
                ThreePointArc((-6, 19.101020514), (-8.288252998, 17.546595612), (-11, 17))
                Line((-11, 17), (-6, 17))
                Line((-6, 17), (-6, 19.101020514))
            make_face()
        # profile 6 of 9: a face of its own
        with BuildSketch(Plane.ZY.offset(75)):
            with BuildLine():
                Line((6, 19.101020514), (6, 28.898979486))
                ThreePointArc((6, 28.898979486), (4, 24), (6, 19.101020514))
            make_face()
        # profile 7 of 9: a face of its own
        with BuildSketch(Plane.ZY.offset(75)):
            with BuildLine():
                ThreePointArc((18, 24), (15.949747468, 28.949747468), (11, 31))
                ThreePointArc((11, 31), (8.288252998, 30.453404388), (6, 28.898979486))
                Line((6, 28.898979486), (6, 19.101020514))
                ThreePointArc((6, 19.101020514), (8.288252998, 17.546595612), (11, 17))
                ThreePointArc((11, 17), (15.949747468, 19.050252532), (18, 24))
            make_face()
            with Locations((11, 24)):
                Circle(TUBE_BOSS_SKETCH_R, mode=Mode.SUBTRACT)
        # profile 8 of 9: a face of its own
        with BuildSketch(Plane.ZY.offset(75)):
            with BuildLine():
                Line((6, 19.101020514), (6, 17))
                Line((6, 17), (11, 17))
                ThreePointArc((11, 17), (8.288252998, 17.546595612), (6, 19.101020514))
            make_face()
        # profile 9 of 9: a face of its own
        with BuildSketch(Plane.ZY.offset(75)):
            with BuildLine():
                Line((11, 31), (6, 31))
                Line((6, 31), (6, 28.898979486))
                ThreePointArc((6, 28.898979486), (8.288252998, 30.453404388), (11, 31))
            make_face()
        extrude(amount=-TUBE_BOSS_DEPTH)

    # Tube Bore Sketch → Tube Bore Cut (cut)
    with SkipClean():  # the faces are left unmerged after this step: merging them gives an invalid solid
        with BuildSketch(Plane.ZY.offset(75)):
            with Locations((-11, 24)):
                Circle(TUBE_BORE_SKETCH_R)
            with Locations((11, 24)):
                Circle(TUBE_BORE_SKETCH_R)
        extrude(amount=-TUBE_BORE_CUT_DEPTH, mode=Mode.SUBTRACT)


solid = part.part
